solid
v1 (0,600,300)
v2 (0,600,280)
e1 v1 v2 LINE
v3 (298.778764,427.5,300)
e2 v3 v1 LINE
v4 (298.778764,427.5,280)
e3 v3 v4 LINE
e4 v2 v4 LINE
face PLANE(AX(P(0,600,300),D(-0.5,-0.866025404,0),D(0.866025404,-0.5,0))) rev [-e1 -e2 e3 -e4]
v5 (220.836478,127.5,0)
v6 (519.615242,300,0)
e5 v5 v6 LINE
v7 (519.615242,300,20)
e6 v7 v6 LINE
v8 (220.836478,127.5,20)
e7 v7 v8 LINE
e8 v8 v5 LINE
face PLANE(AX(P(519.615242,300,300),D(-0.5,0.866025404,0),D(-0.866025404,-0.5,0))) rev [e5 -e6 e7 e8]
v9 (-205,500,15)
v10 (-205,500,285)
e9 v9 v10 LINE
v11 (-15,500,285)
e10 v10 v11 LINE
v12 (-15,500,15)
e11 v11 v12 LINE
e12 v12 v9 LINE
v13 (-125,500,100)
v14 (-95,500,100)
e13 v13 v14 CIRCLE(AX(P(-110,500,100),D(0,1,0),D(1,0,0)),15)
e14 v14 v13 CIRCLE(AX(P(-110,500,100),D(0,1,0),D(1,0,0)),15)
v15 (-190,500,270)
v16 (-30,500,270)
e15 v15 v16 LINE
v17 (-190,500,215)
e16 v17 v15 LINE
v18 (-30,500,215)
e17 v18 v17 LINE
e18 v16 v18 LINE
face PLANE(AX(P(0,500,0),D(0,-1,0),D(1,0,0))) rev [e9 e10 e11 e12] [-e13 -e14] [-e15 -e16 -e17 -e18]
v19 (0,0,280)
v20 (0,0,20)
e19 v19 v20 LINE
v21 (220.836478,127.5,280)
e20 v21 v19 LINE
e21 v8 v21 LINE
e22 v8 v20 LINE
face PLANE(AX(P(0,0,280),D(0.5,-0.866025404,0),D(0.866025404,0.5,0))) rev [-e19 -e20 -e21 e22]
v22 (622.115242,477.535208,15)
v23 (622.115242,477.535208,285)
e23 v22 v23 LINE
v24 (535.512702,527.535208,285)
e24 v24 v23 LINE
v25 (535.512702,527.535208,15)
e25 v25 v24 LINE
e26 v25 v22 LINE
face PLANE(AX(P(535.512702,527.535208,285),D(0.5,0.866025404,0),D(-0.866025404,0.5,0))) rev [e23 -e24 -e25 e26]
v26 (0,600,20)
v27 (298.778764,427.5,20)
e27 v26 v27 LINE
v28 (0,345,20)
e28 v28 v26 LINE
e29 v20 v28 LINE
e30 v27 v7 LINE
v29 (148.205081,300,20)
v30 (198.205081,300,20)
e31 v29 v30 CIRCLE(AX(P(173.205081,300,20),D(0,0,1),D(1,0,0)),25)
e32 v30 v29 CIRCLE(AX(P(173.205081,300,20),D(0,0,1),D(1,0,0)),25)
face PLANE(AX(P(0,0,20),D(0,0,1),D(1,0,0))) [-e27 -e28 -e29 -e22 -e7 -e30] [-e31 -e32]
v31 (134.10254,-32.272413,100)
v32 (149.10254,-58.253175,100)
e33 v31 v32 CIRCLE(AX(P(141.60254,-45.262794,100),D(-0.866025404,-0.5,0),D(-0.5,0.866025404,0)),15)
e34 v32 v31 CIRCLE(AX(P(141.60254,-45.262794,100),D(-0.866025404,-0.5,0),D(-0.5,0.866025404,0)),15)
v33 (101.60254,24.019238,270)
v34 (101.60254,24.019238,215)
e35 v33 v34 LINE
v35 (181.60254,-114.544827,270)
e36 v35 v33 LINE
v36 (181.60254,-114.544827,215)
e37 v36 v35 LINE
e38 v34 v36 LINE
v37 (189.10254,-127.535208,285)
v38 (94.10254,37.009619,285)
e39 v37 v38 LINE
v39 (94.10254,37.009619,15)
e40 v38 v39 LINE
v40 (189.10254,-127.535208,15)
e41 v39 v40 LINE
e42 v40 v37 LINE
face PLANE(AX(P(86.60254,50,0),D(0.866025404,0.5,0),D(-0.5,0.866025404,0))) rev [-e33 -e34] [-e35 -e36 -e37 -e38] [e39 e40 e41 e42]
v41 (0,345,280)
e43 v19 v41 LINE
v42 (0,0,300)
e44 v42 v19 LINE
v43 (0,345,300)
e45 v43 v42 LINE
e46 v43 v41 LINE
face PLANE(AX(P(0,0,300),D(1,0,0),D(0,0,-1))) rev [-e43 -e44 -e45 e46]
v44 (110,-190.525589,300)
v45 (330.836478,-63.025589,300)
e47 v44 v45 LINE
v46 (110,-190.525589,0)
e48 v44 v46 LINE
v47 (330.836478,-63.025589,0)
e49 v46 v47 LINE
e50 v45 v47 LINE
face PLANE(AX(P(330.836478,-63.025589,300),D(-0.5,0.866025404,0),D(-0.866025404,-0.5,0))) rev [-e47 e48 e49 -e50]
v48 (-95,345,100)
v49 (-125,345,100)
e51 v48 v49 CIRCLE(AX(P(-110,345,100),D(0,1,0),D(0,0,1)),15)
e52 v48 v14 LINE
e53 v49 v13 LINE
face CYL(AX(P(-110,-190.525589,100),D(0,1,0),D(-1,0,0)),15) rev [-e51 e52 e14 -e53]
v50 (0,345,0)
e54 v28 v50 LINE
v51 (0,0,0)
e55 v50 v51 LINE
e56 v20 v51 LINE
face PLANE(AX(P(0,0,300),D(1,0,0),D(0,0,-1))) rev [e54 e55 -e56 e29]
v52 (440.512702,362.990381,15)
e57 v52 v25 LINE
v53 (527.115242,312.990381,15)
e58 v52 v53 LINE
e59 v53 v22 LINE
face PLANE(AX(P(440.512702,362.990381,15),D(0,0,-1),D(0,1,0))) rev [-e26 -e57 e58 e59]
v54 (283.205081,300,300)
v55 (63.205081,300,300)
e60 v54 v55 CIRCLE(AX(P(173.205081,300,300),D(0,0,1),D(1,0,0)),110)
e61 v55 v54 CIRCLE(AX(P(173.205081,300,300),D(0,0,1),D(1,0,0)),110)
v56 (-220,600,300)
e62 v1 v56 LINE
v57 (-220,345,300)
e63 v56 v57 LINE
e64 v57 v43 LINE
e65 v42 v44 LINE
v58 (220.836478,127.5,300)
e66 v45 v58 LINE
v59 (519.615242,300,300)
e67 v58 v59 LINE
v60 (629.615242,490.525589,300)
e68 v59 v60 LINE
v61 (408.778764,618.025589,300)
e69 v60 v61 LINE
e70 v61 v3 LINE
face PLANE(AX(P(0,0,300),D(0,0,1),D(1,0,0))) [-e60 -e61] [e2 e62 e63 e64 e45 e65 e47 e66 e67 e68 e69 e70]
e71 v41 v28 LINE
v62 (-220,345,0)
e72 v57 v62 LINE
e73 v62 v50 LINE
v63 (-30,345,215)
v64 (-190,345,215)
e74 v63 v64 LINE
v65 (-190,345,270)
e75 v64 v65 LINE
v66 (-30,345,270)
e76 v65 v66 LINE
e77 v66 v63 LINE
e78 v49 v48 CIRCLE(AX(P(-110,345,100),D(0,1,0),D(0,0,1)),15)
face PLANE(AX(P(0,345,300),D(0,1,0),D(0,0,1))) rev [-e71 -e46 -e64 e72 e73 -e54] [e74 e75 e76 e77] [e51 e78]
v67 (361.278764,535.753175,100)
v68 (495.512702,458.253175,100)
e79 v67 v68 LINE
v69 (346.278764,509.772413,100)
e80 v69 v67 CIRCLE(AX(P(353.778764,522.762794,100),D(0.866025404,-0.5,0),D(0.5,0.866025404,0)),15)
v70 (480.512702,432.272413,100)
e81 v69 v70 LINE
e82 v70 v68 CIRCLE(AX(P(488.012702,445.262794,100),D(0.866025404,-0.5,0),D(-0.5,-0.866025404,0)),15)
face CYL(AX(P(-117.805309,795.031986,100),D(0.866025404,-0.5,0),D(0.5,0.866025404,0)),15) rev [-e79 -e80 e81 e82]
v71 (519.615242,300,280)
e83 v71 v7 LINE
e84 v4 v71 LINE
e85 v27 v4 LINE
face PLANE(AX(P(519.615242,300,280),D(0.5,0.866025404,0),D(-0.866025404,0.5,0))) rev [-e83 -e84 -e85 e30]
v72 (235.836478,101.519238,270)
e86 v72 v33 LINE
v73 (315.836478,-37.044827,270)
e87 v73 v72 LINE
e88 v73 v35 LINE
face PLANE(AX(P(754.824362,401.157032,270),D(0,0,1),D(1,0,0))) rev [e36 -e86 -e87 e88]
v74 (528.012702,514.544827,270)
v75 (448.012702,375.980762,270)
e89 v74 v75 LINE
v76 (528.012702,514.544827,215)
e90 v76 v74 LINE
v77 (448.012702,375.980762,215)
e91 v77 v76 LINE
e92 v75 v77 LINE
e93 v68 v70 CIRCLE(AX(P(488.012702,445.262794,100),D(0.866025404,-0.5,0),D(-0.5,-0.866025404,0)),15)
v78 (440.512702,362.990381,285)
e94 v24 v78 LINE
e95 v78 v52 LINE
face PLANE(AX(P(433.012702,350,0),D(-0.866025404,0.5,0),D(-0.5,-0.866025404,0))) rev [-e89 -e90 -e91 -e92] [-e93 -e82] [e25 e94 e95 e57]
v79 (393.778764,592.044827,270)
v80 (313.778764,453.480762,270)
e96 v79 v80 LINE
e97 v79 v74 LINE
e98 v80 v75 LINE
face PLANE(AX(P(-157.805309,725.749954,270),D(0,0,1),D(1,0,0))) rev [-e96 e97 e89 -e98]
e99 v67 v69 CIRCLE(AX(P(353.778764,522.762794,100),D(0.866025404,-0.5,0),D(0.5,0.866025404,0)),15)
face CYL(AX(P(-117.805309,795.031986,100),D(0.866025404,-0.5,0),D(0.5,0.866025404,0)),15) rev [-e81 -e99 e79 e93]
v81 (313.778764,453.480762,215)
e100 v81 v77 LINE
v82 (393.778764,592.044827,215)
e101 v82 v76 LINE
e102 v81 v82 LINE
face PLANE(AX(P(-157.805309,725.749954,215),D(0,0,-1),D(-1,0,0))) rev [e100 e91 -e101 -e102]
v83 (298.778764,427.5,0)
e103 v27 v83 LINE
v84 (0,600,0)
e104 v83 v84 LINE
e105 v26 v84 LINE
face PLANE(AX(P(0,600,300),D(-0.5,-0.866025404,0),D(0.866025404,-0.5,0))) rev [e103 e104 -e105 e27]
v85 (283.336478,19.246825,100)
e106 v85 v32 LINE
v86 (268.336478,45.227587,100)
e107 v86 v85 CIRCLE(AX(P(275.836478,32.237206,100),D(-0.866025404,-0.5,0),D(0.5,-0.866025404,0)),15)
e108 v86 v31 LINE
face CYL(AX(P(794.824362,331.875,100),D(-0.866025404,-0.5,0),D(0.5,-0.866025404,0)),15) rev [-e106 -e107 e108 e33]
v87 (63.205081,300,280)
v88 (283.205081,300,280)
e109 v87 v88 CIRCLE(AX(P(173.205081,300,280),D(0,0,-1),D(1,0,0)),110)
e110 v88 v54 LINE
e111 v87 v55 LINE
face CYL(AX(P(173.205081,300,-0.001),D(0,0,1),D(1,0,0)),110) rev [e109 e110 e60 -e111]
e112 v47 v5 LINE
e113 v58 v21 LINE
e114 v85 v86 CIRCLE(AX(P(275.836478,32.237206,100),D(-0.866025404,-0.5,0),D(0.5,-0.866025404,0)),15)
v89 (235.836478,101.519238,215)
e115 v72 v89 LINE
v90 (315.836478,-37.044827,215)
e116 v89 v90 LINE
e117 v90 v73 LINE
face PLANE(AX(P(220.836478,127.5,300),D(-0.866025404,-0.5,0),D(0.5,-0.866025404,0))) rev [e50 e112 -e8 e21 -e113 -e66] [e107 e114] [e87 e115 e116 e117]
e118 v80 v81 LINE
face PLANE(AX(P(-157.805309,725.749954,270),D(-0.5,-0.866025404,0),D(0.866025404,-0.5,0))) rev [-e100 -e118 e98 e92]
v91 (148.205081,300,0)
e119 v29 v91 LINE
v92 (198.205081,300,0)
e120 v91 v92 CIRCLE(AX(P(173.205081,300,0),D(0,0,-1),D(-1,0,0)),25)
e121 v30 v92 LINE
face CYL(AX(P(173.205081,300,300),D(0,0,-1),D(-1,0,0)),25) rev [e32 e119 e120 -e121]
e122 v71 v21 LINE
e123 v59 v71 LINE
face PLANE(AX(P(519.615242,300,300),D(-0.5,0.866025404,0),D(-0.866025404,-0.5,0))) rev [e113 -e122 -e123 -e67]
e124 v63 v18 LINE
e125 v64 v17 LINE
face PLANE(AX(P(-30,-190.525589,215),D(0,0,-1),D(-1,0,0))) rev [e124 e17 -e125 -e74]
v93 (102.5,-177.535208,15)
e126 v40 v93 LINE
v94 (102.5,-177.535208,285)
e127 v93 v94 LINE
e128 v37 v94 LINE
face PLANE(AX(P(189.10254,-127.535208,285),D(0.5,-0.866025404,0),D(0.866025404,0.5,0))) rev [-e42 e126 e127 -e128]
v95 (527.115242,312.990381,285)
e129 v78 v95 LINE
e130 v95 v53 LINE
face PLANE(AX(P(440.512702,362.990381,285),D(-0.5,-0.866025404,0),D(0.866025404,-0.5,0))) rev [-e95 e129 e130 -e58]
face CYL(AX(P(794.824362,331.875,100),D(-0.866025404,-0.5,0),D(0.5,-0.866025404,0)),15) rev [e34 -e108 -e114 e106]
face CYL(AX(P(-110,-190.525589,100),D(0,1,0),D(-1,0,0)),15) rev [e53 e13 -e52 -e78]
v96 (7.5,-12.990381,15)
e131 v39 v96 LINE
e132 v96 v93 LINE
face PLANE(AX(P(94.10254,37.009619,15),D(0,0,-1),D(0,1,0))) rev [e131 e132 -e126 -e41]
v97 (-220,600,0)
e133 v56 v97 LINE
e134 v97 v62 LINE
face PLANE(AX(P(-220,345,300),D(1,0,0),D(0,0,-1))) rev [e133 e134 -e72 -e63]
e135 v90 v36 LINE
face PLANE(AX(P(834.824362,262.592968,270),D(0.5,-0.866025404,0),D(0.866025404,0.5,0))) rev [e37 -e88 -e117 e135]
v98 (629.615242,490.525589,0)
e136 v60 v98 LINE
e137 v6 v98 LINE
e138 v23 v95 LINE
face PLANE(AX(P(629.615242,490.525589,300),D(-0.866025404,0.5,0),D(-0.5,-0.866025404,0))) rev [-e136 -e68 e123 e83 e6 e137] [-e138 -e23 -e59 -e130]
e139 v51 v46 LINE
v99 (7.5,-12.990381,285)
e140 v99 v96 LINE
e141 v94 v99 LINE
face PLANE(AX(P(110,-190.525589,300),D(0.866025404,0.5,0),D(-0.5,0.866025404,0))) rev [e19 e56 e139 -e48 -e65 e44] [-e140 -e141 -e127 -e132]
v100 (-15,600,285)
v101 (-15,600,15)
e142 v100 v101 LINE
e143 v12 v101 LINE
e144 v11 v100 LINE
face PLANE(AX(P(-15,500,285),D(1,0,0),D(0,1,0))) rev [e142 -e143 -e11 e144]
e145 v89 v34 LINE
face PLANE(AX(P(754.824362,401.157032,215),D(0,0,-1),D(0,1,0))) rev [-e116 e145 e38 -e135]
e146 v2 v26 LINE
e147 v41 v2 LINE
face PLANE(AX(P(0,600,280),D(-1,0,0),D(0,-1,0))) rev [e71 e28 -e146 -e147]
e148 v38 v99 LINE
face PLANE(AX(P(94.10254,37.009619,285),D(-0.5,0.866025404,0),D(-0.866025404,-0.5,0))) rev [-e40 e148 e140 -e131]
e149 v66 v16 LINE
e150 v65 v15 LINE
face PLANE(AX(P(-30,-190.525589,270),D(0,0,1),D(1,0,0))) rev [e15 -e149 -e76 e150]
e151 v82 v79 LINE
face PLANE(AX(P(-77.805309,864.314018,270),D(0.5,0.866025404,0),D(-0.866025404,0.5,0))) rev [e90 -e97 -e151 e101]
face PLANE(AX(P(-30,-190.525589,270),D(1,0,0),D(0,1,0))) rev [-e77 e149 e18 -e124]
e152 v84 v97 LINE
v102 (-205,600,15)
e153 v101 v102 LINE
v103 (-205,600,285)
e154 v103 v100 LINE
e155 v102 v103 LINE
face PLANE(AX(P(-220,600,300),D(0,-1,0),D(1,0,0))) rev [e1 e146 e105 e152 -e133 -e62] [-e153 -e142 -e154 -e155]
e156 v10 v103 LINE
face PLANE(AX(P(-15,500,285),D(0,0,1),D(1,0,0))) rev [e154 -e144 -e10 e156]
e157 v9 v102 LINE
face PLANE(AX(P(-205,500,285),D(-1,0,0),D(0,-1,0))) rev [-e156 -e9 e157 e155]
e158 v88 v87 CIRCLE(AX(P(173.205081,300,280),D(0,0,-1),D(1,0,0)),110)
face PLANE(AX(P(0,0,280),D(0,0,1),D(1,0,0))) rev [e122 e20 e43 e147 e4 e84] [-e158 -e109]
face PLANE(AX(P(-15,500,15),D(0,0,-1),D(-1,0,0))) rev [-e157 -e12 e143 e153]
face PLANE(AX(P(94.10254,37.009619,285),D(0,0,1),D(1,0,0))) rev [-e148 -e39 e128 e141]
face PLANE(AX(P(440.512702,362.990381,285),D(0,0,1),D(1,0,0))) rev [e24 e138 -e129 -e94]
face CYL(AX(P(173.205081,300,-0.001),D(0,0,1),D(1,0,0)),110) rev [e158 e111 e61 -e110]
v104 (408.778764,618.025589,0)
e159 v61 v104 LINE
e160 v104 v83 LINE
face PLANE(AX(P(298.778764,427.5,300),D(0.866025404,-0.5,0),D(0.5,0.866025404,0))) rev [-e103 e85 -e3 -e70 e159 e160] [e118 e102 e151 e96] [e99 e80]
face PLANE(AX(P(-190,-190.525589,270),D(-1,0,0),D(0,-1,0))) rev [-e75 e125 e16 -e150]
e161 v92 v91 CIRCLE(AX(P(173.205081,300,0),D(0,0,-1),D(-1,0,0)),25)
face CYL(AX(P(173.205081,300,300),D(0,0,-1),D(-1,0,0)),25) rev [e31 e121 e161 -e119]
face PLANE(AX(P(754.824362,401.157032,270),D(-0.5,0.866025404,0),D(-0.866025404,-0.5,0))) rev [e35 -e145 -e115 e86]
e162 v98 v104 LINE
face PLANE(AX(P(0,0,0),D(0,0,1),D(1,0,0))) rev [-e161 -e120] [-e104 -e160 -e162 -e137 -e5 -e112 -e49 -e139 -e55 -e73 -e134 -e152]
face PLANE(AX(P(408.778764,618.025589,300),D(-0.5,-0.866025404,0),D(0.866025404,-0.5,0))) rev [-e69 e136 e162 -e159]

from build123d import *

# Parameters (mm, degrees)
BOSS_EXTRUDE1_DEPTH = 300
CUT_EXTRUDE2_START  = -20
CUT_EXTRUDE2_DEPTH  = 260
SKETCH3_R           = 25
CUT_EXTRUDE3_DEPTH  = 932.86425071
SKETCH4_R           = 15
SKETCH4_W           = 55
SKETCH4_H           = 160
CUT_EXTRUDE4_DEPTH  = 932.86425071
SKETCH5_R           = 15
SKETCH5_W           = 160
SKETCH5_H           = 55
CUT_EXTRUDE5_DEPTH  = 1055.203993494
SKETCH7_R           = 15
SKETCH7_W           = 55
SKETCH7_H           = 160
CUT_EXTRUDE6_DEPTH  = 954.980428731
CUT_EXTRUDE7_REACH  = 933.864
SKETCH8_R           = 110
SKETCH9_W           = 270
SKETCH9_H           = 190
CUT_EXTRUDE8_DEPTH  = 100
CIRPATTERN1_COUNT   = 3


with BuildPart() as part:
    # Sketch1 → Boss-Extrude1 (new body)
    with BuildSketch(Plane.XY):
        Polygon((0, 0), (0, 345), (-220, 345), (-220, 600), (0, 600), (298.778764306, 427.5), (408.778764306, 618.025588833), (629.615242271, 490.525588833), (519.615242271, 300), (220.836477965, 127.5), (330.836477965, -63.025588833), (110, -190.525588833), align=None)
    extrude(amount=BOSS_EXTRUDE1_DEPTH)

    # Sketch2 → Cut-Extrude2 (cut)
    with BuildSketch(Plane(origin=(0, 0, 0), x_dir=(-1, 0, 0), z_dir=(0, 0, -1)).offset(CUT_EXTRUDE2_START)):
        Polygon((0, 600), (0, 0), (-519.615242271, 300), align=None)
    extrude(amount=-CUT_EXTRUDE2_DEPTH, mode=Mode.SUBTRACT)

    # Sketch3 → Cut-Extrude3 (cut, through all)
    with BuildSketch(Plane(origin=(0, 0, 0), x_dir=(-1, 0, 0), z_dir=(0, 0, -1))):
        with Locations((-173.205080757, 300)):
            Circle(SKETCH3_R)
    extrude(amount=-CUT_EXTRUDE3_DEPTH, mode=Mode.SUBTRACT)

    # Sketch4 → Cut-Extrude4 (cut, through all)
    with BuildSketch(Plane(origin=(0, 0, 0), x_dir=(0, 0, 1), z_dir=(-0.866025403784456, -0.4999999999999701, 0))):
        with Locations(Location((100, -110, 0), (0, 0, 270))):
            Circle(SKETCH4_R)
        with Locations((242.5, -110)):
            Rectangle(SKETCH4_W, SKETCH4_H)
    extrude(amount=-CUT_EXTRUDE4_DEPTH, mode=Mode.SUBTRACT)

    # Sketch5 → Cut-Extrude5 (cut, through all)
    with BuildSketch(Plane(origin=(0, 600, 0), x_dir=(1, 0, 0), z_dir=(0, 1, 0))):
        with Locations(Location((-110, -100, 0), (0, 0, 180))):
            Circle(SKETCH5_R)
        with Locations((-110, -242.5)):
            Rectangle(SKETCH5_W, SKETCH5_H)
    extrude(amount=-CUT_EXTRUDE5_DEPTH, mode=Mode.SUBTRACT)

    # Sketch7 → Cut-Extrude6 (cut, through all)
    with BuildSketch(Plane(origin=(259.807621135, -150, 0), x_dir=(0, 0, -1), z_dir=(0.8660254037844342, -0.5000000000000079, 0))):
        with Locations(Location((-100, 629.615242271, 0), (0, 0, 90))):
            Circle(SKETCH7_R)
        with Locations((-242.5, 629.615242271)):
            Rectangle(SKETCH7_W, SKETCH7_H)
    extrude(amount=-CUT_EXTRUDE6_DEPTH, mode=Mode.SUBTRACT)

    # Sketch8 → Cut-Extrude7 (cut, up to next)
    with BuildSketch(Plane.XY.offset(300), mode=Mode.PRIVATE) as cut_extrude7_sk1:
        with Locations((173.205080757, 300)):
            Circle(SKETCH8_R)
    cut_extrude7_tool1 = extrude(cut_extrude7_sk1.sketch, amount=-CUT_EXTRUDE7_REACH, mode=Mode.PRIVATE) & part.part
    add(cut_extrude7_tool1.solids().sort_by_distance((173.205081, 300, 300))[0], mode=Mode.SUBTRACT)

    # Sketch9 → Cut-Extrude8 (cut)
    with BuildSketch(Plane(origin=(0, 0, 0), x_dir=(0, 0, 1), z_dir=(-0.866025403784456, -0.4999999999999701, 0))):
        with Locations((150, -110)):
            Rectangle(SKETCH9_W, SKETCH9_H)
    cut_extrude8 = extrude(amount=-CUT_EXTRUDE8_DEPTH, mode=Mode.SUBTRACT)

    # CirPattern1: Cut-Extrude8 ×3 about axis
    cirpattern1_axis = Axis((173.205080757, 300, 0), (0, 0, 1))
    for i in range(1, CIRPATTERN1_COUNT):
        add(cut_extrude8.rotate(cirpattern1_axis, i * 360 / CIRPATTERN1_COUNT), mode=Mode.SUBTRACT)


solid = part.part
